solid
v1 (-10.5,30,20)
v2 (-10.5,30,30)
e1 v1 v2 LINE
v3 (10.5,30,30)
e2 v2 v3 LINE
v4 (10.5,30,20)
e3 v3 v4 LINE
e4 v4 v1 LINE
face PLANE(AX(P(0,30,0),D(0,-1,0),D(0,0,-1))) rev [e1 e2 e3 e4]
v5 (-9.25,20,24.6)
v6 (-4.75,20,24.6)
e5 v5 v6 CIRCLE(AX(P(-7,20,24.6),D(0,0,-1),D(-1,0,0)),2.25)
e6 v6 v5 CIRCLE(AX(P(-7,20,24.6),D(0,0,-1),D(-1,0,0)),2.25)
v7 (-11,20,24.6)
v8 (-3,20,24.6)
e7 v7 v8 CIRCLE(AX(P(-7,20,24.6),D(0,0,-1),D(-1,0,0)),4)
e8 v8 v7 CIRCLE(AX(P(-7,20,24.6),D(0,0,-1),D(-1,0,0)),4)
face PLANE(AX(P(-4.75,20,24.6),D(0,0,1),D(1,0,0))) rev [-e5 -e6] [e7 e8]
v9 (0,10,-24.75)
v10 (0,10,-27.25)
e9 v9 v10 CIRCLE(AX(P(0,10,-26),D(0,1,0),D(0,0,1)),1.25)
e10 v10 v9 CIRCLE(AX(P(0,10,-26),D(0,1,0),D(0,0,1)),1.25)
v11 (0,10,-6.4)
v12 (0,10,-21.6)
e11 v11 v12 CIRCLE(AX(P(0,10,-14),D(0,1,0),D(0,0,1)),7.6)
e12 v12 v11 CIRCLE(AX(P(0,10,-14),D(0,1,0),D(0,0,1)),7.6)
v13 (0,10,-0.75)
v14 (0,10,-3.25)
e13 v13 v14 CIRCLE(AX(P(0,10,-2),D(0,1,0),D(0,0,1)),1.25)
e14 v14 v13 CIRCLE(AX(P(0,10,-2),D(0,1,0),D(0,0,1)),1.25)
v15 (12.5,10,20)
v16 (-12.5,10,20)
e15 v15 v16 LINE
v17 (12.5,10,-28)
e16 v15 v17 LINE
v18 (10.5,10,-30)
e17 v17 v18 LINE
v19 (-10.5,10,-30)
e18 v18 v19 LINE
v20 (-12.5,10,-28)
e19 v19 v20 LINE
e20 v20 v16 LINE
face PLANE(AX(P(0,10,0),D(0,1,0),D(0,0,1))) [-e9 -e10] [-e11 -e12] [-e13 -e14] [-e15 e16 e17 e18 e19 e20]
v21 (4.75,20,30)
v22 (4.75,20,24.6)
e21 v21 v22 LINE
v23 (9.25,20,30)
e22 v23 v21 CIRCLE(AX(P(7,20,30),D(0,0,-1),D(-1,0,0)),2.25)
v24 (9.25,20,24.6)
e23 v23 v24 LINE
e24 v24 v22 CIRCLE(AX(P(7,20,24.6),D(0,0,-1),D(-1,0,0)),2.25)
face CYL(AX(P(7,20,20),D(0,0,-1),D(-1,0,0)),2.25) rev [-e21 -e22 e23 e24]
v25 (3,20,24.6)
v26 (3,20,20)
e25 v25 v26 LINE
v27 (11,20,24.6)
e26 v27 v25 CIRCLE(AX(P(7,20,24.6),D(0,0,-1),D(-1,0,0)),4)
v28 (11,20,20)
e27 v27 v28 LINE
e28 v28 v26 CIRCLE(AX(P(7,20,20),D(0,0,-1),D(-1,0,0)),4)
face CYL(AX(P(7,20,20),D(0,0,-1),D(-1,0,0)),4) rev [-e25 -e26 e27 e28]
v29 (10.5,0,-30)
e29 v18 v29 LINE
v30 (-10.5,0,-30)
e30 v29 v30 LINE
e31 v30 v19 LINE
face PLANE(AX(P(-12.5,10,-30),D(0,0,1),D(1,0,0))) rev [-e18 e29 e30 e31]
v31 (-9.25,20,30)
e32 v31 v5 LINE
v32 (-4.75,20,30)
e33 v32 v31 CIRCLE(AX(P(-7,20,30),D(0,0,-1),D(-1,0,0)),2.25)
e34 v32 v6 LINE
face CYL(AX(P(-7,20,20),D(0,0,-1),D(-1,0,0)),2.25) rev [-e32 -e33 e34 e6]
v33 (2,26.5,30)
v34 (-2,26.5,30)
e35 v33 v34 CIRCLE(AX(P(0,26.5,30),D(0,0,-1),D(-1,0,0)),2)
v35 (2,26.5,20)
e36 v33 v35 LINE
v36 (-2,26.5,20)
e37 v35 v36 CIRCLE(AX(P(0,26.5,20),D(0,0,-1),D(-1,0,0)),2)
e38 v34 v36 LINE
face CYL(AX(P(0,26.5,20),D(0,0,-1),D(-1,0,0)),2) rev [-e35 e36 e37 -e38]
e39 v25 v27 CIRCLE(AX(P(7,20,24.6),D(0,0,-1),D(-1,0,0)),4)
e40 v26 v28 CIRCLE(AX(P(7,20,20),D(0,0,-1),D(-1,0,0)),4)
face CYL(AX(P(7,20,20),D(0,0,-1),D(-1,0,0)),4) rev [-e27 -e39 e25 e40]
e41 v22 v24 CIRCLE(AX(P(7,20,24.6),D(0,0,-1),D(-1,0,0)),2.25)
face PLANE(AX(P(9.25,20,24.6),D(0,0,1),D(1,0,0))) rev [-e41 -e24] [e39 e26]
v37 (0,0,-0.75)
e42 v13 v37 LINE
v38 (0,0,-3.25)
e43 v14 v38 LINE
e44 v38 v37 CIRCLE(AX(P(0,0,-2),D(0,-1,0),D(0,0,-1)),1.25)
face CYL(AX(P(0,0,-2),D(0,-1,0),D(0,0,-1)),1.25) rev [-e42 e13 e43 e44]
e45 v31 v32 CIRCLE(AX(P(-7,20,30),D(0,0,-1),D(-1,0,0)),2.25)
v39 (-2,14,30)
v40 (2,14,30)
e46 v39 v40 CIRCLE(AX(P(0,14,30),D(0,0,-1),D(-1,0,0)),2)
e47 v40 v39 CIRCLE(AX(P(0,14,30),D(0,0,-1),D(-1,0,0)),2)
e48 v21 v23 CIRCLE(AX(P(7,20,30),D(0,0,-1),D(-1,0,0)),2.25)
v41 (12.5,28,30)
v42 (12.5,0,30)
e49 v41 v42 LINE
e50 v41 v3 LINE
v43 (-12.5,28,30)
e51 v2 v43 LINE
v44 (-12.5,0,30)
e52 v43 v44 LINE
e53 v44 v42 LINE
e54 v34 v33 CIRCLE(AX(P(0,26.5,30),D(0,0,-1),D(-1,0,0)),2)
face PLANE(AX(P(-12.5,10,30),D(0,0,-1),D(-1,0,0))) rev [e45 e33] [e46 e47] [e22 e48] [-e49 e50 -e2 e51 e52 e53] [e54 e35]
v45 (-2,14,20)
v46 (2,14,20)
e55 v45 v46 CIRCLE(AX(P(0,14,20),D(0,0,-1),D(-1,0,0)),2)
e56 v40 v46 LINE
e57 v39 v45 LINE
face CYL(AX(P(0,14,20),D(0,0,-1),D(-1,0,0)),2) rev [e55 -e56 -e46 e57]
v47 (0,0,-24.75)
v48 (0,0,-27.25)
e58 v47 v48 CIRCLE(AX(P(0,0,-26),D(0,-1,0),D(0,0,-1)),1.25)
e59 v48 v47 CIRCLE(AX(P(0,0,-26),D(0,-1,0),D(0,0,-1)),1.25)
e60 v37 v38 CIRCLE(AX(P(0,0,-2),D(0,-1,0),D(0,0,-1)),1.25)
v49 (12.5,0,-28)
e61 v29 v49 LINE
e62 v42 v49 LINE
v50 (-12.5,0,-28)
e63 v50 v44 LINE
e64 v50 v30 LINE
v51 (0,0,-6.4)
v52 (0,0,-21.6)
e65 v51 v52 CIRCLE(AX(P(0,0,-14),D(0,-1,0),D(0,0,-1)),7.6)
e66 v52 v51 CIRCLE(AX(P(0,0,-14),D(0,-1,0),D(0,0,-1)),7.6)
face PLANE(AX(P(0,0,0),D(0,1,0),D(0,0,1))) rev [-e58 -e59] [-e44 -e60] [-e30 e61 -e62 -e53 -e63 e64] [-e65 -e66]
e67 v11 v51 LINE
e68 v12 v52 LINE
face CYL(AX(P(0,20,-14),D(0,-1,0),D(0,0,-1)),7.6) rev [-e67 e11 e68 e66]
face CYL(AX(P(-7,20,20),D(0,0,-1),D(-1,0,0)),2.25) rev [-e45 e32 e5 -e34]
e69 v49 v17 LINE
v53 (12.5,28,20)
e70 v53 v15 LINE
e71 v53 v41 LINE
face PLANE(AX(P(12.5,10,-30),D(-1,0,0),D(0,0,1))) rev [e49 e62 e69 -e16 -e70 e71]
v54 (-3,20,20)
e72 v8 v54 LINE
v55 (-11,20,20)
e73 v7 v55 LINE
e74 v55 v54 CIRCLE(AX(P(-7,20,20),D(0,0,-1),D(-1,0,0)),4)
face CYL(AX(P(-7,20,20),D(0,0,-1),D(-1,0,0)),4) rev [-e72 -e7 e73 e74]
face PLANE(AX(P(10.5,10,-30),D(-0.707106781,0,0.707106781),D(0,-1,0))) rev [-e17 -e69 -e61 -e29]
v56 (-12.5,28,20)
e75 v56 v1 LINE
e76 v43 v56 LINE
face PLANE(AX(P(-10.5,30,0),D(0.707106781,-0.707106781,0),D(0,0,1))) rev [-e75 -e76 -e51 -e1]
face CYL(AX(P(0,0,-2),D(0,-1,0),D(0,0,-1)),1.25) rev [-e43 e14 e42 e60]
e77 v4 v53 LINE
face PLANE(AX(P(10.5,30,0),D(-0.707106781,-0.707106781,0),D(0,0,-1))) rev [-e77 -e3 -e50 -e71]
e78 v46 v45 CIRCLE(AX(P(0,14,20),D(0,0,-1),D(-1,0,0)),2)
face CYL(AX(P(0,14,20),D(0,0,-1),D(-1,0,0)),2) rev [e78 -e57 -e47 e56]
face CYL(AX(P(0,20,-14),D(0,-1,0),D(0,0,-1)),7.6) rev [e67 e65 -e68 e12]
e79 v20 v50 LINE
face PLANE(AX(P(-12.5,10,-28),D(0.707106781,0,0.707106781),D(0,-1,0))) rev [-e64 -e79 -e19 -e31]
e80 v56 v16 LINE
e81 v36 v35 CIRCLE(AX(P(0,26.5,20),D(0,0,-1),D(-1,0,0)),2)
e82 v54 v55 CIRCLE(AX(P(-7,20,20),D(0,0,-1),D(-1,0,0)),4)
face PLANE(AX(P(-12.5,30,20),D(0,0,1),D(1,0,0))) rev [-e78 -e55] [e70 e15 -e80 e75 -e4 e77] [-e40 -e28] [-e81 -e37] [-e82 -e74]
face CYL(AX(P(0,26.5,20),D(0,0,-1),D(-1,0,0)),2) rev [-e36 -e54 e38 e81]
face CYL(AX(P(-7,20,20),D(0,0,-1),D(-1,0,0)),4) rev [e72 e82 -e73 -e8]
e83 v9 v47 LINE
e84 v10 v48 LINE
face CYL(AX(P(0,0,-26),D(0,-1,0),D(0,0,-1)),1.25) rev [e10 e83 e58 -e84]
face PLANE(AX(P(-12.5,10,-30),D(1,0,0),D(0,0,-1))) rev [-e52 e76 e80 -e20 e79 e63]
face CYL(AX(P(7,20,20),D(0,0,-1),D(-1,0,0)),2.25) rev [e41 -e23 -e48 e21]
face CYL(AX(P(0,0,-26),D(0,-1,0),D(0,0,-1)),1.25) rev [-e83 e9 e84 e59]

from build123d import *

# Parameters (mm, degrees)
SKETCH_1_W                = 25
SKETCH_1_H                = 60
EXTRUDE_1_DEPTH           = 10
SKETCH_2_R                = 7.6
CUT_EXTRUDE_1_DEPTH       = 20
SKETCH_3_W                = 25
SKETCH_3_H                = 10
EXTRUDE_2_DEPTH           = 20
CHAMFER_1_SIZE            = 2
HOLE_WIZARD_1_D           = 4.5
HOLE_WIZARD_1_DEPTH       = 15
HOLE_WIZARD_1_CBORE_D     = 8
HOLE_WIZARD_1_CBORE_DEPTH = 4.6
HOLE_WIZARD_1_TIP         = 1.351936393
MM_1_D                    = 4
MM_1_DEPTH                = 15
MM_1_TIP                  = 1.201721238
HOLE_WIZARD_M3_1_D        = 2.5
HOLE_WIZARD_M3_1_DEPTH    = 15
HOLE_WIZARD_M3_1_TIP      = 0.751075774


with BuildPart() as part:
    # 草图1 → 凸台-拉伸1 (new body)
    with BuildSketch(Plane(origin=(0, 0, 0), x_dir=(1, 0, 0), z_dir=(0, 1, 0))):
        Rectangle(SKETCH_1_W, SKETCH_1_H)
    extrude(amount=EXTRUDE_1_DEPTH)

    # 草图2 → 切除-拉伸1 (cut)
    with BuildSketch(Plane.XZ):
        with Locations(Location((0, -14, 0), (0, 0, 270))):
            Circle(SKETCH_2_R)
    extrude(amount=-CUT_EXTRUDE_1_DEPTH, mode=Mode.SUBTRACT)

    # 草图3 → 凸台-拉伸2 (add)
    with BuildSketch(Plane(origin=(0, 10, 0), x_dir=(1, 0, 0), z_dir=(0, 1, 0))):
        with Locations((0, -25)):
            Rectangle(SKETCH_3_W, SKETCH_3_H)
    extrude(amount=EXTRUDE_2_DEPTH)

    # 倒角1
    chamfer_1_edges = [part.edges().sort_by_distance(p)[0] for p in [
        (-12.5, 30, 25),
        (12.5, 30, 25),
        (-12.5, 5, -30),
        (12.5, 5, -30),
    ]]
    chamfer(chamfer_1_edges, length=CHAMFER_1_SIZE)

    # 打孔尺寸(%根据)内六角圆柱头螺钉的类型1
    with Locations(Plane(origin=(0, 0, 20), x_dir=(-1, 0, 0), z_dir=(0, 0, -1))):
        with Locations((7, 20), (-7, 20)):
            CounterBoreHole(HOLE_WIZARD_1_D / 2, HOLE_WIZARD_1_CBORE_D / 2, HOLE_WIZARD_1_CBORE_DEPTH, depth=HOLE_WIZARD_1_DEPTH)
            with Locations((0, 0, -(HOLE_WIZARD_1_DEPTH + HOLE_WIZARD_1_TIP / 2))):  # 118° drill point
                Cone(0, HOLE_WIZARD_1_D / 2, HOLE_WIZARD_1_TIP, mode=Mode.SUBTRACT)

    # 大小mm 暗销孔1
    with Locations(Plane(origin=(0, 0, 20), x_dir=(-1, 0, 0), z_dir=(0, 0, -1))):
        with Locations((0, 26.5), (0, 14)):
            Hole(MM_1_D / 2, depth=MM_1_DEPTH)
            with Locations((0, 0, -(MM_1_DEPTH + MM_1_TIP / 2))):  # 118° drill point
                Cone(0, MM_1_D / 2, MM_1_TIP, mode=Mode.SUBTRACT)

    # M3 螺纹孔1
    with Locations(Plane(origin=(0, 0, 0), x_dir=(-1, 0, 0), z_dir=(0, -1, 0))):
        with Locations((0, 26), (0, 2)):
            Hole(HOLE_WIZARD_M3_1_D / 2, depth=HOLE_WIZARD_M3_1_DEPTH)
            with Locations((0, 0, -(HOLE_WIZARD_M3_1_DEPTH + HOLE_WIZARD_M3_1_TIP / 2))):  # 118° drill point
                Cone(0, HOLE_WIZARD_M3_1_D / 2, HOLE_WIZARD_M3_1_TIP, mode=Mode.SUBTRACT)


solid = part.part
